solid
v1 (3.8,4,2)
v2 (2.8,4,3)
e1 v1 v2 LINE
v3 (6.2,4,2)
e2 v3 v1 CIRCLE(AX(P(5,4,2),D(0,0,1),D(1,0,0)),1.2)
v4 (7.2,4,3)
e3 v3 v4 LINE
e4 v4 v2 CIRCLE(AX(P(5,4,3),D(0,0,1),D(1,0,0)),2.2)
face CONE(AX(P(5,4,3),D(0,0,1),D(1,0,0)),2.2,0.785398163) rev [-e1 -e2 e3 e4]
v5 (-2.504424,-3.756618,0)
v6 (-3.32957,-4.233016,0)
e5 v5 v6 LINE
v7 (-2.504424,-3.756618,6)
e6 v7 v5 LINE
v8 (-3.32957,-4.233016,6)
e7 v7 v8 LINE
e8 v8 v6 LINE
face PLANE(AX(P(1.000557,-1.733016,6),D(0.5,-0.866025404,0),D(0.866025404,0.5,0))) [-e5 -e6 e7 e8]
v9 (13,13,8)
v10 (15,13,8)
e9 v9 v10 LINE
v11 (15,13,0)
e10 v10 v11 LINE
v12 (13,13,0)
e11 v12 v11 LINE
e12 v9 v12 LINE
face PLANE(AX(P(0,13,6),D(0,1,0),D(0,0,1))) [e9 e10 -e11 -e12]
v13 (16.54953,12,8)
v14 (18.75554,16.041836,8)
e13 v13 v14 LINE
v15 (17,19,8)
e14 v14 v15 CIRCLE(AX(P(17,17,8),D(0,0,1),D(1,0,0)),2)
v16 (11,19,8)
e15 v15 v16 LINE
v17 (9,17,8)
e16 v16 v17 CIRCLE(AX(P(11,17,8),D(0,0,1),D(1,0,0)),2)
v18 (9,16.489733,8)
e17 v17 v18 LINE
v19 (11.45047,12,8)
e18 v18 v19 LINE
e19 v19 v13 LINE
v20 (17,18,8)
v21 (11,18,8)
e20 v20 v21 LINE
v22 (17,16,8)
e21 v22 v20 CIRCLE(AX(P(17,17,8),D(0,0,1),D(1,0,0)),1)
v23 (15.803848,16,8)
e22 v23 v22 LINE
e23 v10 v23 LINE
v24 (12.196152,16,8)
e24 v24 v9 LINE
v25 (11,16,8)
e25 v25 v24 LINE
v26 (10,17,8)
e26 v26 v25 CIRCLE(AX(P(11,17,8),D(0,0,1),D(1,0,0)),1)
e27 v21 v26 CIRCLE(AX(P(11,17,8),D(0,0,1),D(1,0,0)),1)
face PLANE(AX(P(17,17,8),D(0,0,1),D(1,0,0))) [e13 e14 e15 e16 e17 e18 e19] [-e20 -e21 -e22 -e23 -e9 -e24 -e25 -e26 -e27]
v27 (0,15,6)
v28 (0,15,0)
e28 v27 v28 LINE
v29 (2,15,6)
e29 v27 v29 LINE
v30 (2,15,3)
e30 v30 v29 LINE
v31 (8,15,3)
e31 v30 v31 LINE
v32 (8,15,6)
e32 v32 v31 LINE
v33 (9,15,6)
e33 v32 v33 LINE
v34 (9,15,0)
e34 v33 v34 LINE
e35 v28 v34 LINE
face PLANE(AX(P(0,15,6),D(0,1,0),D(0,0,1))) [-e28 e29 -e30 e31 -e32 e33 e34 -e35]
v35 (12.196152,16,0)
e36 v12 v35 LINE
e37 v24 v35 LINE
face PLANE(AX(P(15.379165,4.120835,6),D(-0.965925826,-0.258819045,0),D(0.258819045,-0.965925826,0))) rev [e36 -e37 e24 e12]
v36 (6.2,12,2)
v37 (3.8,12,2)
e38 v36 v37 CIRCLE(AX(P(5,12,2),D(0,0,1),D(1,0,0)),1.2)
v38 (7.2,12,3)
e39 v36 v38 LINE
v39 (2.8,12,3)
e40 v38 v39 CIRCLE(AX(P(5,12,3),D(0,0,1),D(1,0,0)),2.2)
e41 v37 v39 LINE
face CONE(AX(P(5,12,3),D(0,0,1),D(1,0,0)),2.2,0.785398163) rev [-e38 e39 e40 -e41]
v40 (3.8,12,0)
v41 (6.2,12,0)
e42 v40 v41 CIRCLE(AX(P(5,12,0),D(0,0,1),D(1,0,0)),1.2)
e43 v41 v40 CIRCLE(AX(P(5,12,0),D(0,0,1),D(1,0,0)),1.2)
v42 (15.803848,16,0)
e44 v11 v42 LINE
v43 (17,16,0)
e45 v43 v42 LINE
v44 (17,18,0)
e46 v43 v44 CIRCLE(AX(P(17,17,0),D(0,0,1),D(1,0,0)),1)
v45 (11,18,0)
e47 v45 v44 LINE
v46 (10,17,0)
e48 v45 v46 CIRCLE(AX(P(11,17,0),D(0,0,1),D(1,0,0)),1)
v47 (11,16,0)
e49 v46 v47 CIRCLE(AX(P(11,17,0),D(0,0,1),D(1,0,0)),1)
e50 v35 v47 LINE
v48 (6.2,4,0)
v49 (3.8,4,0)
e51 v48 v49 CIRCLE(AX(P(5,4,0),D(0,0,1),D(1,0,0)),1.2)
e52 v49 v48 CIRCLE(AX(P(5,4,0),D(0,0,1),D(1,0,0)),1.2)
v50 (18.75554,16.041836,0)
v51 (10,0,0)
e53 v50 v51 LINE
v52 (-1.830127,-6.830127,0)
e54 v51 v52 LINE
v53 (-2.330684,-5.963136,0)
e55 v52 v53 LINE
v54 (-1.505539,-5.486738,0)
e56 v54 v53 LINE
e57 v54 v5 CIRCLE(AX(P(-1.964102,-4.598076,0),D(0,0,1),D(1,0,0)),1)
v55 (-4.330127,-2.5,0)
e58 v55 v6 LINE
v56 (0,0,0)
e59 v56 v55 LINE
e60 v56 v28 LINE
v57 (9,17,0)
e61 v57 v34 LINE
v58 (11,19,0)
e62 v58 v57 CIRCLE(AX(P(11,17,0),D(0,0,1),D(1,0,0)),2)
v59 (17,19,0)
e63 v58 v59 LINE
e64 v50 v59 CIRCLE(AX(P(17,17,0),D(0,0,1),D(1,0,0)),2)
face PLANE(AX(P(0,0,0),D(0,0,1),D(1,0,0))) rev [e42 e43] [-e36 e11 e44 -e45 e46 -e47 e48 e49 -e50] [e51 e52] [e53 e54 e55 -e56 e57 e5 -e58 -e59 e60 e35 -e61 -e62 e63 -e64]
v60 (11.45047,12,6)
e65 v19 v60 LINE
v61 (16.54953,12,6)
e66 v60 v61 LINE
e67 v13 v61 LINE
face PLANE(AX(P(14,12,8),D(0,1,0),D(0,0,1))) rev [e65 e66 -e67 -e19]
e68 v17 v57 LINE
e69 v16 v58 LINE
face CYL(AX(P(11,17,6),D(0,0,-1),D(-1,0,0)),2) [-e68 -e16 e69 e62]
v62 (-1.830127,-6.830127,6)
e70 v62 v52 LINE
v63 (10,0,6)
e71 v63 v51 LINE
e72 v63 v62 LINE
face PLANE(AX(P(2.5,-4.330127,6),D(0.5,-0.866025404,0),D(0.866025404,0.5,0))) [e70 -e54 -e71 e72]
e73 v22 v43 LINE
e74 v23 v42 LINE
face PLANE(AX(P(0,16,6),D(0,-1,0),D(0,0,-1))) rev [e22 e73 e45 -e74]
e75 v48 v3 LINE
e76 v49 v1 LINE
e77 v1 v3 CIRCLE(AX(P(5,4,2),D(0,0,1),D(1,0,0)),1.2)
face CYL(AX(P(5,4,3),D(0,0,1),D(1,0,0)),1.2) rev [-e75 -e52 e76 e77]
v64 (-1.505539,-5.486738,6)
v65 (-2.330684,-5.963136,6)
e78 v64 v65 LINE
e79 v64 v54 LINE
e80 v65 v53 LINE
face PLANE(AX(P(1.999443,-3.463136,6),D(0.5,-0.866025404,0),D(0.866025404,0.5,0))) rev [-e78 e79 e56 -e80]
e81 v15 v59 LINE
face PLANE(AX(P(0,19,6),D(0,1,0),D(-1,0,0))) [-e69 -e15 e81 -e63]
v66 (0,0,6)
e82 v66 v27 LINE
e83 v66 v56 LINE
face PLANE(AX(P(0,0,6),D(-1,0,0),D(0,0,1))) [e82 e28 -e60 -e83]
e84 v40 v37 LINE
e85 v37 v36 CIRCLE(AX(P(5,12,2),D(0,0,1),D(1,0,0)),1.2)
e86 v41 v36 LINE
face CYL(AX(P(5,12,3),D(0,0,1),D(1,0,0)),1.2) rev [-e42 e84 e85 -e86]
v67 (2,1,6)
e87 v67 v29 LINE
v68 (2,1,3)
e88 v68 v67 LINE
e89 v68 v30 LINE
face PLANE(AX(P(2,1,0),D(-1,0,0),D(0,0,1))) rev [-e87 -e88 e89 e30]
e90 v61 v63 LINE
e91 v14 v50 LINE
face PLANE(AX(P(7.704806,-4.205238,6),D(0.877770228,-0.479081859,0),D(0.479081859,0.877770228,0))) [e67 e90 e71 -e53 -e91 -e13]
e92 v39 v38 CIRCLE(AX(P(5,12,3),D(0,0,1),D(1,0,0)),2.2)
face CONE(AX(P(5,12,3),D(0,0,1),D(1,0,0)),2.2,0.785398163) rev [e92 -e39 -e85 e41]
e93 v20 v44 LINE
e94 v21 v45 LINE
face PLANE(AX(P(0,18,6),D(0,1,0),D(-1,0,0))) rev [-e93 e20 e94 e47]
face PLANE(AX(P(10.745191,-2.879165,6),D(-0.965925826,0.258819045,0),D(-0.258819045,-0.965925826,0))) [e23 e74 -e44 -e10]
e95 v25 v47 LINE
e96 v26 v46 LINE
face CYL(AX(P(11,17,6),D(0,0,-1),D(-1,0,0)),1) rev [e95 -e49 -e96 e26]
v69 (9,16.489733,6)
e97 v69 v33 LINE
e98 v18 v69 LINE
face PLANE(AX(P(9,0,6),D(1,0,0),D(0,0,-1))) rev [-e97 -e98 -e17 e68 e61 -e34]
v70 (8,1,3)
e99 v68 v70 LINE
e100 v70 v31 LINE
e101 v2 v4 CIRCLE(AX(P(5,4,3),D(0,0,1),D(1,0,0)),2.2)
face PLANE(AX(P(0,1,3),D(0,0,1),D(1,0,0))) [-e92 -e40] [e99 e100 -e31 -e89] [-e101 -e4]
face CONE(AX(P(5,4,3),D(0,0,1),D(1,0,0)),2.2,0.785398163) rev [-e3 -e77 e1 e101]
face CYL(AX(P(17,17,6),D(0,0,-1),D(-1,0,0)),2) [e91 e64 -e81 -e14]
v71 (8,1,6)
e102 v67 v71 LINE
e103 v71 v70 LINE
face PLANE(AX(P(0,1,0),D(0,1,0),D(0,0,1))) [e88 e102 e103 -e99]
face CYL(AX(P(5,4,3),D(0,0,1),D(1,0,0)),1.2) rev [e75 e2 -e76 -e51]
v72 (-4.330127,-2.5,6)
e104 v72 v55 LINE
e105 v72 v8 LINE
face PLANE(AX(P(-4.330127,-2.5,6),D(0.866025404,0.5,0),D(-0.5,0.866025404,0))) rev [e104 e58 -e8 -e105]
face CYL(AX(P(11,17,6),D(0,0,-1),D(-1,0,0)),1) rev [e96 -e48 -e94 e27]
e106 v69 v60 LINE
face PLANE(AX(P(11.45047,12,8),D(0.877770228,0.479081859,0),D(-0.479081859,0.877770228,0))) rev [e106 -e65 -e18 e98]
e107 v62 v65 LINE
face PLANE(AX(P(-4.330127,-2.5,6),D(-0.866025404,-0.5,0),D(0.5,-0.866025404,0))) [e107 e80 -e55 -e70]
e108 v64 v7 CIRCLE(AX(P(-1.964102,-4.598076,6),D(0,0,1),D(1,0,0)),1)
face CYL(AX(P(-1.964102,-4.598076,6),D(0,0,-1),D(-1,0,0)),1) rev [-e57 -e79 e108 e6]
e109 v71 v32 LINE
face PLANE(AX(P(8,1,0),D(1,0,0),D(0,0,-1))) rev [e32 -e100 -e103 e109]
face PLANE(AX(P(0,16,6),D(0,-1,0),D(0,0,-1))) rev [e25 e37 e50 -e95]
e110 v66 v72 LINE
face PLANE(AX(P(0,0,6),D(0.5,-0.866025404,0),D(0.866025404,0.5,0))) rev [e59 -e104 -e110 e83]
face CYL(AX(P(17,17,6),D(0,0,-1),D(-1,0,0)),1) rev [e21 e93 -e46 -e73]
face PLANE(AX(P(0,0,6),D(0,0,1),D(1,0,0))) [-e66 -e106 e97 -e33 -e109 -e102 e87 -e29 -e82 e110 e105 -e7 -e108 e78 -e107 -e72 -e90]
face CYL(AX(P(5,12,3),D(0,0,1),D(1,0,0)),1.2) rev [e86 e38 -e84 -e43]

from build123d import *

# Parameters (mm, degrees)
L_BRACKET_BODY_DEPTH             = 6
TRAPEZOID_SLOT_BOSS_DEPTH        = 2
POCKET_CUT_DEPTH                 = 14
M2_COUNTERSUNK_HOLES_D           = 2.4
M2_COUNTERSUNK_HOLES_CSINK_D     = 4.4
M2_COUNTERSUNK_HOLES_CSINK_ANGLE = 90


with BuildPart() as part:
    # L Bracket Profile Sketch → L Bracket Body (new body)
    # profile 1 of 2: a face of its own
    with BuildSketch(Plane.XY):
        with BuildLine():
            Line((0, 15), (0, 0))
            Line((0, 0), (-4.330127019, -2.5))
            Line((-4.330127019, -2.5), (-3.329569645, -4.233016207))
            Line((-3.329569645, -4.233016207), (-2.504424414, -3.756618386))
            ThreePointArc((-2.504424414, -3.756618386), (-1.098076211, -4.098076211), (-1.505539161, -5.486738395))
            Line((-1.505539161, -5.486738395), (-2.330684392, -5.963136216))
            Line((-2.330684392, -5.963136216), (-1.830127019, -6.830127019))
            Line((-1.830127019, -6.830127019), (10, 0))
            Line((10, 0), (16.549529843, 12))
            Line((16.549529843, 12), (14, 12))
            Line((14, 12), (11.450470157, 12))
            Line((11.450470157, 12), (9.244459544, 16.041836283))
            ThreePointArc((9.244459544, 16.041836283), (9.062078315, 16.505571497), (9, 17))
            Line((9, 17), (9, 15))
            Line((9, 15), (0, 15))
        make_face()
    # profile 2 of 2: a face of its own
    with BuildSketch(Plane.XY):
        with BuildLine():
            ThreePointArc((11, 19), (9.585786438, 18.414213562), (9, 17))
            ThreePointArc((9, 17), (9.062078315, 16.505571497), (9.244459544, 16.041836283))
            Line((9.244459544, 16.041836283), (11.450470157, 12))
            Line((11.450470157, 12), (14, 12))
            Line((14, 12), (16.549529843, 12))
            Line((16.549529843, 12), (18.755540456, 16.041836283))
            ThreePointArc((18.755540456, 16.041836283), (18.719931312, 18.020703817), (17, 19))
            Line((17, 19), (11, 19))
        make_face()
        with BuildLine():
            Line((15, 13), (13, 13))
            Line((13, 13), (12.196152423, 16))
            Line((12.196152423, 16), (11, 16))
            ThreePointArc((11, 16), (10, 17), (11, 18))
            Line((11, 18), (17, 18))
            ThreePointArc((17, 18), (18, 17), (17, 16))
            Line((17, 16), (15.803847577, 16))
            Line((15.803847577, 16), (15, 13))
        make_face(mode=Mode.SUBTRACT)
    extrude(amount=L_BRACKET_BODY_DEPTH)

    # Trapezoid Slot Boss Sketch → Trapezoid Slot Boss (add)
    with BuildSketch(Plane.XY.offset(6)):
        with BuildLine():
            Line((14, 12), (16.549529843, 12))
            Line((16.549529843, 12), (18.755540456, 16.041836283))
            ThreePointArc((18.755540456, 16.041836283), (18.719931312, 18.020703817), (17, 19))
            Line((17, 19), (11, 19))
            ThreePointArc((11, 19), (9.585786438, 18.414213562), (9, 17))
            Line((9, 17), (9, 16.489733247))
            Line((9, 16.489733247), (11.450470157, 12))
            Line((11.450470157, 12), (14, 12))
        make_face()
        with BuildLine():
            Line((11, 18), (17, 18))
            ThreePointArc((17, 18), (18, 17), (17, 16))
            Line((17, 16), (15.803847577, 16))
            Line((15.803847577, 16), (15, 13))
            Line((15, 13), (13, 13))
            Line((13, 13), (12.196152423, 16))
            Line((12.196152423, 16), (11, 16))
            ThreePointArc((11, 16), (10, 17), (11, 18))
        make_face(mode=Mode.SUBTRACT)
    extrude(amount=TRAPEZOID_SLOT_BOSS_DEPTH)

    # Pocket Cut Sketch → Pocket Cut (cut)
    with BuildSketch(Plane(origin=(0, 15, 0), x_dir=(1, 0, 0), z_dir=(0, 1, 0))):
        Polygon((2, -3), (2, -6), (5, -6), (8, -6), (8, -3), (5, -3), align=None)
    extrude(amount=-POCKET_CUT_DEPTH, mode=Mode.SUBTRACT)

    # M2 Countersunk Holes (through all)
    with Locations(Plane.XY.offset(3)):
        with Locations((5, 12), (5, 4)):
            CounterSinkHole(M2_COUNTERSUNK_HOLES_D / 2, M2_COUNTERSUNK_HOLES_CSINK_D / 2, counter_sink_angle=M2_COUNTERSUNK_HOLES_CSINK_ANGLE)


solid = part.part
